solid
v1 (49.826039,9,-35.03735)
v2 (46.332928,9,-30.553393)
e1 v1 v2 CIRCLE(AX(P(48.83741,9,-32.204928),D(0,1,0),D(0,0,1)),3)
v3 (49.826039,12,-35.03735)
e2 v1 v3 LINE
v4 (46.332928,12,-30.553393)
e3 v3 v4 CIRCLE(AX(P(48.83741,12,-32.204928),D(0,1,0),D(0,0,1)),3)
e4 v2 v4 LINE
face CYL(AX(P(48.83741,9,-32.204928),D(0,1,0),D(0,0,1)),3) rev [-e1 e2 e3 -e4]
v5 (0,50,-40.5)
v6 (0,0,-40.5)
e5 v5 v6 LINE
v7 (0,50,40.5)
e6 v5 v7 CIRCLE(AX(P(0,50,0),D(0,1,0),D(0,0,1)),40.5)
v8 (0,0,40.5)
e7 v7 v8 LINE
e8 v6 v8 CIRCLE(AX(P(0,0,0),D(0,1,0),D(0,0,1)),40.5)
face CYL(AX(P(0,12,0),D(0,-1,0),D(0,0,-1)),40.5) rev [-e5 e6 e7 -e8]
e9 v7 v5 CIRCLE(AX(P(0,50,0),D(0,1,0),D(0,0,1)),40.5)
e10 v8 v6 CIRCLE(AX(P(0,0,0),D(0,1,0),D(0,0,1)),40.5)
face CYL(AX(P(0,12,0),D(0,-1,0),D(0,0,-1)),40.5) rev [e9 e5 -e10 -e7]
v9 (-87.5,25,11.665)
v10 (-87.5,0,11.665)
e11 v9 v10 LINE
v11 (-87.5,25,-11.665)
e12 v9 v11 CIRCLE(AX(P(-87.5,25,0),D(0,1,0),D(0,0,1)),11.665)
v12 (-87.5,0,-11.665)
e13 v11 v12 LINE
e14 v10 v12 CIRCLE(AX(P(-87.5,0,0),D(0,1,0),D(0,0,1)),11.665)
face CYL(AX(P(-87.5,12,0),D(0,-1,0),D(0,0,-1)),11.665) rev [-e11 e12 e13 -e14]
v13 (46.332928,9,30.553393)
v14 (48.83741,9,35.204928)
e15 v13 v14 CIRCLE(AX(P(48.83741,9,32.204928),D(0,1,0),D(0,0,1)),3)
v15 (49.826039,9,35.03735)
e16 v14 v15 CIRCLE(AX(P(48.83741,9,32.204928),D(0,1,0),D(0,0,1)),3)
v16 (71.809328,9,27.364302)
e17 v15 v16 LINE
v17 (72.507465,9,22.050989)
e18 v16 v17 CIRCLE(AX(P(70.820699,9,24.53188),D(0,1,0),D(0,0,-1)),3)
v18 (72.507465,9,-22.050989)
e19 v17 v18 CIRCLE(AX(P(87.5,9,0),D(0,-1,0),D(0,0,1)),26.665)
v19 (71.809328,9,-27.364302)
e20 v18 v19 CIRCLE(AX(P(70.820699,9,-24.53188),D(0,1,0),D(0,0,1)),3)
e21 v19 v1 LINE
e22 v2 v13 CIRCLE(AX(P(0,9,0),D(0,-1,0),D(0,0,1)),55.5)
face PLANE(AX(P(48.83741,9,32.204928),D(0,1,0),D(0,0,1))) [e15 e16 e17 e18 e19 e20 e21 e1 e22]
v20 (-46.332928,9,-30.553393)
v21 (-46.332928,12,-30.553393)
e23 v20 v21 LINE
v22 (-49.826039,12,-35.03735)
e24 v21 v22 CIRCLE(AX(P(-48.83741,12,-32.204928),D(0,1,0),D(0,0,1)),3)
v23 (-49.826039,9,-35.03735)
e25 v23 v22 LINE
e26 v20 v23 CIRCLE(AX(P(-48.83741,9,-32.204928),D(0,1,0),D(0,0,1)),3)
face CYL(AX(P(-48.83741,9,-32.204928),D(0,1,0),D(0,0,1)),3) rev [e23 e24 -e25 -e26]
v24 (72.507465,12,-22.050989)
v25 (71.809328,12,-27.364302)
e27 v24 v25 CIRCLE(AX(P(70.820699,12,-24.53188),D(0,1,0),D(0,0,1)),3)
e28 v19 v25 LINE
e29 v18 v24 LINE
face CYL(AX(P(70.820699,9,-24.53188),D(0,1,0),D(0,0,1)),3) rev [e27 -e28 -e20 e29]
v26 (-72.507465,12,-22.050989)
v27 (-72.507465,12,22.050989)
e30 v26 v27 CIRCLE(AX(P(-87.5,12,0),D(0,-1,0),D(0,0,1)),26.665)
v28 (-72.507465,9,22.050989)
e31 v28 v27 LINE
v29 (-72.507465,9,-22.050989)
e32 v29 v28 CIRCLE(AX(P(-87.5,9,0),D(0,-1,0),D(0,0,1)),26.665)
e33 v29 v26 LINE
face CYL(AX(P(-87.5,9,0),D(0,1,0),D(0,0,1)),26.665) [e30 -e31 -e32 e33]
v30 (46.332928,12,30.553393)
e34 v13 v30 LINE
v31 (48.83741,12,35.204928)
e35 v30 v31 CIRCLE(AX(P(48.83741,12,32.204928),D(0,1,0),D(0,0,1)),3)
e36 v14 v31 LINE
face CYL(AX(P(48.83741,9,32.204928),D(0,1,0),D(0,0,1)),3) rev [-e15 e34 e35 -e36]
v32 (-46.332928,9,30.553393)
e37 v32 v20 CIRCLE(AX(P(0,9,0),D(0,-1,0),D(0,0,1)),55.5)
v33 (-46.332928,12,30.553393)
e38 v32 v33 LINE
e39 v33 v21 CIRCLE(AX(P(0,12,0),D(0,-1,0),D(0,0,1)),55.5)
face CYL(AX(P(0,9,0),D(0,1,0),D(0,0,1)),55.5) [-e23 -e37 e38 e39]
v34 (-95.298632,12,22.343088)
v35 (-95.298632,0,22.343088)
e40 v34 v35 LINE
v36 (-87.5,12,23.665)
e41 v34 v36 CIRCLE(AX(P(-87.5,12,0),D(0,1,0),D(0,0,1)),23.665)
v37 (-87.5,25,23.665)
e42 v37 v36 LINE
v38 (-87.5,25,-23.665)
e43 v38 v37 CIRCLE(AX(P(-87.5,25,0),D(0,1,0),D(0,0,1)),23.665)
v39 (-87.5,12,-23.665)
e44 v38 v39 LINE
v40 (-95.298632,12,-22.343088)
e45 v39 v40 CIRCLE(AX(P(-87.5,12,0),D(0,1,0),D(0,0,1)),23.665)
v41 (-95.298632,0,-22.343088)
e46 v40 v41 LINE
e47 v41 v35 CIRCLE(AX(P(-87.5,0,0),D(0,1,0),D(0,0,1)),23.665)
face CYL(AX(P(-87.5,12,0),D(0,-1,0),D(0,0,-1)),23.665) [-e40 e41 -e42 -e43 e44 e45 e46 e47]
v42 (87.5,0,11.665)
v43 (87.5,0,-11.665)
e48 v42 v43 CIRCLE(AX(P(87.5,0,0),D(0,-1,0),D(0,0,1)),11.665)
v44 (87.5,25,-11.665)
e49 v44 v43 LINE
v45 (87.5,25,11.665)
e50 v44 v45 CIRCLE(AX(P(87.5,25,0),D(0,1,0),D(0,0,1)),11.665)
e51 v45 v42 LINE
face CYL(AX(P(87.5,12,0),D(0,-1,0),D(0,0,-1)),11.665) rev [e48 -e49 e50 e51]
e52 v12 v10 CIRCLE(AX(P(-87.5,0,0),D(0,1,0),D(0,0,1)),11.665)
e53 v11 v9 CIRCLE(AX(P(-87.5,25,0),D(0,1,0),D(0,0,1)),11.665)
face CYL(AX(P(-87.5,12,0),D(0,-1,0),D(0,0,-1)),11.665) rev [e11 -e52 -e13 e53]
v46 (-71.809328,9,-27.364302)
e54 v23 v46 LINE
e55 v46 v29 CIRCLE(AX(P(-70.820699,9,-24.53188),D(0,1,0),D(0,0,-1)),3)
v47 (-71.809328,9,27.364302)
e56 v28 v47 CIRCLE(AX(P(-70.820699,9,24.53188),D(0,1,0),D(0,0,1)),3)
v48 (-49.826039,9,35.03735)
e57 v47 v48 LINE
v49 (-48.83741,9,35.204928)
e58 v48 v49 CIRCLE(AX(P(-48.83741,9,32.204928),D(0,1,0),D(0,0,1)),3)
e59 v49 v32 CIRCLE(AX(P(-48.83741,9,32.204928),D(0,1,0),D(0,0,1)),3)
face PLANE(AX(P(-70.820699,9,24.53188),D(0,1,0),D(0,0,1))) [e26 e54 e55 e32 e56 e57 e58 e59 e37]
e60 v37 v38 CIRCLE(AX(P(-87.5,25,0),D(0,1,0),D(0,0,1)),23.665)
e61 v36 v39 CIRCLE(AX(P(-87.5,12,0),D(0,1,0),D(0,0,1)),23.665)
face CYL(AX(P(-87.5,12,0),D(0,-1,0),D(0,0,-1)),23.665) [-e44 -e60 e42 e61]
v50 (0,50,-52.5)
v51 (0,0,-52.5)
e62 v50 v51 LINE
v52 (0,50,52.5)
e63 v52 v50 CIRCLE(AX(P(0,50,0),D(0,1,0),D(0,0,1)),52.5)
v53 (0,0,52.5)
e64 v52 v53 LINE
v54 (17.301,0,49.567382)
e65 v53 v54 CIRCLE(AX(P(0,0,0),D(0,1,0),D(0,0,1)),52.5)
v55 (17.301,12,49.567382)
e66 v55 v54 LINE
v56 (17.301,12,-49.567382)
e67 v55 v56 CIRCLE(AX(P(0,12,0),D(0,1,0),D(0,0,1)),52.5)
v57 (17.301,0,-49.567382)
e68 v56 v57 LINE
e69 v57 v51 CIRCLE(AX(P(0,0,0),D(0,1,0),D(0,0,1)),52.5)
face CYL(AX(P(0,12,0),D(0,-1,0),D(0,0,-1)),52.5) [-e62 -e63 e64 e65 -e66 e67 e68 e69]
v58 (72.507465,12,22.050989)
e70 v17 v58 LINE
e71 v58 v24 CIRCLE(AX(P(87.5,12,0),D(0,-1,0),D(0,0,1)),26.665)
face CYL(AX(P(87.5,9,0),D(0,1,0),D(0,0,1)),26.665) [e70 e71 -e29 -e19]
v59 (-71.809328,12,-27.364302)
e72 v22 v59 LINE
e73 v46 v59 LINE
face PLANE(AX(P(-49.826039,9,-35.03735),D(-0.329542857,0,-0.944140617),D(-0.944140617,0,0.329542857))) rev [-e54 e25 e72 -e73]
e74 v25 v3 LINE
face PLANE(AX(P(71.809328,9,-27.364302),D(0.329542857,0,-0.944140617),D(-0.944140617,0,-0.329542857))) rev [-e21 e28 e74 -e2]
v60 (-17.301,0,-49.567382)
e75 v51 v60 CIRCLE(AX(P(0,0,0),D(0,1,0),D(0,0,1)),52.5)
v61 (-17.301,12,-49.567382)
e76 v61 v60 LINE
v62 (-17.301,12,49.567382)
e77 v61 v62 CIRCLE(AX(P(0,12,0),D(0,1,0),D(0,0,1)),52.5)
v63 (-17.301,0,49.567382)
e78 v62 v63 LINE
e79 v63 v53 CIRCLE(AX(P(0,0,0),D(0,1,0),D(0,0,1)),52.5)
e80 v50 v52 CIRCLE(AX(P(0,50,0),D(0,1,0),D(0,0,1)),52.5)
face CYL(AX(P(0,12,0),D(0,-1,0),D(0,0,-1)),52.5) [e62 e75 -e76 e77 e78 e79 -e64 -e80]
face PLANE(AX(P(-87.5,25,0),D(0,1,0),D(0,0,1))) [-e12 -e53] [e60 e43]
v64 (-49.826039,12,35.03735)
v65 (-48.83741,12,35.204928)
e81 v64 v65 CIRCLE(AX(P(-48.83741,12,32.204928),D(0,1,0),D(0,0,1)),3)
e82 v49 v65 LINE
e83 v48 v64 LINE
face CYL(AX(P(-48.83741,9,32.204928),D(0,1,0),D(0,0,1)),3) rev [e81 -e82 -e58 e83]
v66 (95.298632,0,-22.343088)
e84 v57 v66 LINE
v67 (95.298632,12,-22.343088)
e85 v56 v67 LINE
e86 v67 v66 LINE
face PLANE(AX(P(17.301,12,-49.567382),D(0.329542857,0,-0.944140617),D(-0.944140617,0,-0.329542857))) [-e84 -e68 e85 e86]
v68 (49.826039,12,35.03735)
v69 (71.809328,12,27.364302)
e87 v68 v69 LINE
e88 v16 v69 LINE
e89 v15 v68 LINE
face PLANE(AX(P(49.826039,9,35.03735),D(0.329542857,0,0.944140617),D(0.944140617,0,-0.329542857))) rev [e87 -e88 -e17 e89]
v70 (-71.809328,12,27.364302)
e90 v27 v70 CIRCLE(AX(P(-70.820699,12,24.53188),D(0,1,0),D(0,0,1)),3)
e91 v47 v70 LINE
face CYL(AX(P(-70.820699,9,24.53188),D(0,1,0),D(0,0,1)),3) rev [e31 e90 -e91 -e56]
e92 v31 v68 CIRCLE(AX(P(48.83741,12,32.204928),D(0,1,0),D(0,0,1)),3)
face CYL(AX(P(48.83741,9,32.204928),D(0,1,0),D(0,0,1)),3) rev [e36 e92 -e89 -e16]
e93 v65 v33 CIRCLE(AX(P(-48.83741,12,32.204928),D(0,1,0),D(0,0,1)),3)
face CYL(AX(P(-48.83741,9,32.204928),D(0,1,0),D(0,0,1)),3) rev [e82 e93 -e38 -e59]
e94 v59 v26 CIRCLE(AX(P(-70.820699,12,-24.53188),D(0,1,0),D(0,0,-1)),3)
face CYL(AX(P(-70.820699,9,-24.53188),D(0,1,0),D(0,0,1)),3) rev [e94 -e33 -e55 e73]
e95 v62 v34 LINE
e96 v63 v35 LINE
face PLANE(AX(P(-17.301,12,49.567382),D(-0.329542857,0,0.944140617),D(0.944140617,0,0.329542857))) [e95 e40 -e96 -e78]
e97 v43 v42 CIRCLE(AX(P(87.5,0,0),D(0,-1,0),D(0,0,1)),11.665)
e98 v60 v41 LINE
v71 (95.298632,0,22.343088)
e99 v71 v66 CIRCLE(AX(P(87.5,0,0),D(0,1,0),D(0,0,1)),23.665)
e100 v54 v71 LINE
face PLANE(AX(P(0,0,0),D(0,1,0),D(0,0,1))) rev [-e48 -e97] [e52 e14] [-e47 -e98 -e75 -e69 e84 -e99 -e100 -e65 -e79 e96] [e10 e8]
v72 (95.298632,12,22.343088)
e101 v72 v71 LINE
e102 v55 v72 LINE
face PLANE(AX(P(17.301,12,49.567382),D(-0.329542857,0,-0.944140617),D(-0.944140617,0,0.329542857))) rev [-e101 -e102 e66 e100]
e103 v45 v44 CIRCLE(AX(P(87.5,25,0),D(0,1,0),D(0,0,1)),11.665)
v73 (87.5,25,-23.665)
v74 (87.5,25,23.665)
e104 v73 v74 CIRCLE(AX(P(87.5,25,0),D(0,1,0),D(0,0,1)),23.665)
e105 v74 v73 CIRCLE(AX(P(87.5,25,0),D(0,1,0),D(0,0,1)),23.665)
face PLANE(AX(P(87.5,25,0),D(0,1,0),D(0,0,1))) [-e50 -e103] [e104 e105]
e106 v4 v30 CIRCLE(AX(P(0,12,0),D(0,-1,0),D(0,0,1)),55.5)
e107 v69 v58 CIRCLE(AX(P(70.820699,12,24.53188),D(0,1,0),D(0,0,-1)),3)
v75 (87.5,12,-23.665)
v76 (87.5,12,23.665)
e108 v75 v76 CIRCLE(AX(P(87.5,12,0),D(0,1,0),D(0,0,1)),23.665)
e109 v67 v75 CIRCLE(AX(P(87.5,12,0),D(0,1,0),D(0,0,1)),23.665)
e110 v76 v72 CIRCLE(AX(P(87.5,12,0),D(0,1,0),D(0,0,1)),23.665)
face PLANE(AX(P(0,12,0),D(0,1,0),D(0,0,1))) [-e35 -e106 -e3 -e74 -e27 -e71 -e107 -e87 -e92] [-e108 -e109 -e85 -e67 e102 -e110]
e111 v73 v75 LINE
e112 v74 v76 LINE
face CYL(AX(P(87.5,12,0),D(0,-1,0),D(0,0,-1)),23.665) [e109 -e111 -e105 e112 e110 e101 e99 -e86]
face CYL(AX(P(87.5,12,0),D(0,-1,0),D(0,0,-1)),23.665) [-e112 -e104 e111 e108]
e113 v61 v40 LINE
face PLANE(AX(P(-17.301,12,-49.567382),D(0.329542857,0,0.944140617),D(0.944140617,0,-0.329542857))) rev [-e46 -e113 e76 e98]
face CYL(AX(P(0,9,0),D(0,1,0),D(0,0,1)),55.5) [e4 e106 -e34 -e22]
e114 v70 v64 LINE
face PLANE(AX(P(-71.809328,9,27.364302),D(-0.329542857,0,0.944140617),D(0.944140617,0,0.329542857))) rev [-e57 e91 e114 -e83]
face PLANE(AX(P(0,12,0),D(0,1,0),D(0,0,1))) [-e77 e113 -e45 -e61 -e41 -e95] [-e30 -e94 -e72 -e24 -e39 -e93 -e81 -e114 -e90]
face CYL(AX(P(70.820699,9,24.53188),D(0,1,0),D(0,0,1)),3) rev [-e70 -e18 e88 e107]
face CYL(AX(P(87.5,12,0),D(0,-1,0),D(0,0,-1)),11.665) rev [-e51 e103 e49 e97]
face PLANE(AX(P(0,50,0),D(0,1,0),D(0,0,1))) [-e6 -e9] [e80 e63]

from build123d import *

# Parameters (mm, degrees)
FLANGE_PLATE_SKETCH_R       = 11.665
FLANGE_PLATE_SKETCH_R_2     = 52.5
FLANGE_PLATE_SKETCH_R_3     = 40.5
FLANGE_PLATE_DEPTH          = 12
HOUSING_BOSS_SKETCH_R       = 52.5
HOUSING_BOSS_SKETCH_R_2     = 40.5
BEARING_HOUSING_BOSS_DEPTH  = 38
BOLT_BOSS_SKETCH_R          = 23.665
BOLT_BOSS_SKETCH_R_2        = 11.665
BOLT_BOSSES_2X_DEPTH        = 13
FLANGE_RELIEF_POCKETS_DEPTH = 3


with BuildPart() as part:
    # Flange Plate Sketch → Flange Plate (new body)
    # profile 1 of 3: a face of its own
    with BuildSketch(Plane(origin=(0, 0, 0), x_dir=(1, 0, 0), z_dir=(0, 1, 0))):
        with BuildLine():
            ThreePointArc((-17.301, -49.56738241), (-52.5, 0), (-17.301, 49.56738241))
            Line((-17.301, 49.56738241), (-95.298631714, 22.343087709))
            ThreePointArc((-95.298631714, 22.343087709), (-111.165, 0), (-95.298631714, -22.343087709))
            Line((-95.298631714, -22.343087709), (-17.301, -49.56738241))
        make_face()
        with Locations(Location((-87.5, 0, 0), (0, 0, 270))):
            Circle(FLANGE_PLATE_SKETCH_R, mode=Mode.SUBTRACT)
    # profile 2 of 3: a face of its own
    with BuildSketch(Plane(origin=(0, 0, 0), x_dir=(1, 0, 0), z_dir=(0, 1, 0))):
        with BuildLine():
            Line((95.298631714, 22.343087709), (17.301, 49.56738241))
            ThreePointArc((17.301, 49.56738241), (42.805096075, 30.396936523), (52.5, 0))
            ThreePointArc((52.5, 0), (42.805096075, -30.396936523), (17.301, -49.56738241))
            Line((17.301, -49.56738241), (95.298631714, -22.343087709))
            ThreePointArc((95.298631714, -22.343087709), (111.165, 0), (95.298631714, 22.343087709))
        make_face()
        with Locations(Location((87.5, 0, 0), (0, 0, 270))):
            Circle(FLANGE_PLATE_SKETCH_R, mode=Mode.SUBTRACT)
    # profile 3 of 3: a face of its own
    with BuildSketch(Plane(origin=(0, 0, 0), x_dir=(1, 0, 0), z_dir=(0, 1, 0))):
        Circle(FLANGE_PLATE_SKETCH_R_2)
        with Locations(Location((0, 0, 0), (0, 0, 270))):
            Circle(FLANGE_PLATE_SKETCH_R_3, mode=Mode.SUBTRACT)
    extrude(amount=FLANGE_PLATE_DEPTH)

    # Housing Boss Sketch → Bearing Housing Boss (add)
    with BuildSketch(Plane(origin=(0, 12, 0), x_dir=(1, 0, 0), z_dir=(0, 1, 0))):
        with Locations(Location((0, 0, 0), (0, 0, 109.241031138))):
            Circle(HOUSING_BOSS_SKETCH_R)
        with Locations(Location((0, 0, 0), (0, 0, 270))):
            Circle(HOUSING_BOSS_SKETCH_R_2, mode=Mode.SUBTRACT)
    extrude(amount=BEARING_HOUSING_BOSS_DEPTH)

    # Bolt Boss Sketch → Bolt Bosses 2x (add)
    # profile 1 of 2: a face of its own
    with BuildSketch(Plane(origin=(0, 12, 0), x_dir=(1, 0, 0), z_dir=(0, 1, 0))):
        with Locations(Location((87.5, 0, 0), (0, 0, 70.758968862))):
            Circle(BOLT_BOSS_SKETCH_R)
        with Locations(Location((87.5, 0, 0), (0, 0, 270))):
            Circle(BOLT_BOSS_SKETCH_R_2, mode=Mode.SUBTRACT)
    # profile 2 of 2: a face of its own
    with BuildSketch(Plane(origin=(0, 12, 0), x_dir=(1, 0, 0), z_dir=(0, 1, 0))):
        with Locations(Location((-87.5, 0, 0), (0, 0, 109.241031138))):
            Circle(BOLT_BOSS_SKETCH_R)
        with Locations(Location((-87.5, 0, 0), (0, 0, 270))):
            Circle(BOLT_BOSS_SKETCH_R_2, mode=Mode.SUBTRACT)
    extrude(amount=BOLT_BOSSES_2X_DEPTH)

    # Relief Pocket Sketch → Flange Relief Pockets (cut)
    with BuildSketch(Plane(origin=(0, 12, 0), x_dir=(1, 0, 0), z_dir=(0, 1, 0))):
        with BuildLine():
            Line((71.809327621, 27.364302024), (49.82603874, 35.037349549))
            ThreePointArc((49.82603874, 35.037349549), (46.470783868, 34.048587089), (46.332927596, 30.553392944))
            ThreePointArc((46.332927596, 30.553392944), (55.5, 0), (46.332927596, -30.553392944))
            ThreePointArc((46.332927596, -30.553392944), (46.470783868, -34.048587089), (49.82603874, -35.037349549))
            Line((49.82603874, -35.037349549), (71.809327621, -27.364302024))
            ThreePointArc((71.809327621, -27.364302024), (73.795133067, -24.922702734), (72.507464694, -22.050988869))
            ThreePointArc((72.507464694, -22.050988869), (60.835, 0), (72.507464694, 22.050988869))
            ThreePointArc((72.507464694, 22.050988869), (73.795133067, 24.922702734), (71.809327621, 27.364302024))
        make_face()
        with BuildLine():
            Line((-71.809327621, -27.364302024), (-49.82603874, -35.037349549))
            ThreePointArc((-49.82603874, -35.037349549), (-46.470783868, -34.048587089), (-46.332927596, -30.553392944))
            ThreePointArc((-46.332927596, -30.553392944), (-55.5, 0), (-46.332927596, 30.553392944))
            ThreePointArc((-46.332927596, 30.553392944), (-46.470783868, 34.048587089), (-49.82603874, 35.037349549))
            Line((-49.82603874, 35.037349549), (-71.809327621, 27.364302024))
            ThreePointArc((-71.809327621, 27.364302024), (-73.795133067, 24.922702734), (-72.507464694, 22.050988869))
            ThreePointArc((-72.507464694, 22.050988869), (-60.835, 0), (-72.507464694, -22.050988869))
            ThreePointArc((-72.507464694, -22.050988869), (-73.795133067, -24.922702734), (-71.809327621, -27.364302024))
        make_face()
    extrude(amount=-FLANGE_RELIEF_POCKETS_DEPTH, mode=Mode.SUBTRACT)


solid = part.part
